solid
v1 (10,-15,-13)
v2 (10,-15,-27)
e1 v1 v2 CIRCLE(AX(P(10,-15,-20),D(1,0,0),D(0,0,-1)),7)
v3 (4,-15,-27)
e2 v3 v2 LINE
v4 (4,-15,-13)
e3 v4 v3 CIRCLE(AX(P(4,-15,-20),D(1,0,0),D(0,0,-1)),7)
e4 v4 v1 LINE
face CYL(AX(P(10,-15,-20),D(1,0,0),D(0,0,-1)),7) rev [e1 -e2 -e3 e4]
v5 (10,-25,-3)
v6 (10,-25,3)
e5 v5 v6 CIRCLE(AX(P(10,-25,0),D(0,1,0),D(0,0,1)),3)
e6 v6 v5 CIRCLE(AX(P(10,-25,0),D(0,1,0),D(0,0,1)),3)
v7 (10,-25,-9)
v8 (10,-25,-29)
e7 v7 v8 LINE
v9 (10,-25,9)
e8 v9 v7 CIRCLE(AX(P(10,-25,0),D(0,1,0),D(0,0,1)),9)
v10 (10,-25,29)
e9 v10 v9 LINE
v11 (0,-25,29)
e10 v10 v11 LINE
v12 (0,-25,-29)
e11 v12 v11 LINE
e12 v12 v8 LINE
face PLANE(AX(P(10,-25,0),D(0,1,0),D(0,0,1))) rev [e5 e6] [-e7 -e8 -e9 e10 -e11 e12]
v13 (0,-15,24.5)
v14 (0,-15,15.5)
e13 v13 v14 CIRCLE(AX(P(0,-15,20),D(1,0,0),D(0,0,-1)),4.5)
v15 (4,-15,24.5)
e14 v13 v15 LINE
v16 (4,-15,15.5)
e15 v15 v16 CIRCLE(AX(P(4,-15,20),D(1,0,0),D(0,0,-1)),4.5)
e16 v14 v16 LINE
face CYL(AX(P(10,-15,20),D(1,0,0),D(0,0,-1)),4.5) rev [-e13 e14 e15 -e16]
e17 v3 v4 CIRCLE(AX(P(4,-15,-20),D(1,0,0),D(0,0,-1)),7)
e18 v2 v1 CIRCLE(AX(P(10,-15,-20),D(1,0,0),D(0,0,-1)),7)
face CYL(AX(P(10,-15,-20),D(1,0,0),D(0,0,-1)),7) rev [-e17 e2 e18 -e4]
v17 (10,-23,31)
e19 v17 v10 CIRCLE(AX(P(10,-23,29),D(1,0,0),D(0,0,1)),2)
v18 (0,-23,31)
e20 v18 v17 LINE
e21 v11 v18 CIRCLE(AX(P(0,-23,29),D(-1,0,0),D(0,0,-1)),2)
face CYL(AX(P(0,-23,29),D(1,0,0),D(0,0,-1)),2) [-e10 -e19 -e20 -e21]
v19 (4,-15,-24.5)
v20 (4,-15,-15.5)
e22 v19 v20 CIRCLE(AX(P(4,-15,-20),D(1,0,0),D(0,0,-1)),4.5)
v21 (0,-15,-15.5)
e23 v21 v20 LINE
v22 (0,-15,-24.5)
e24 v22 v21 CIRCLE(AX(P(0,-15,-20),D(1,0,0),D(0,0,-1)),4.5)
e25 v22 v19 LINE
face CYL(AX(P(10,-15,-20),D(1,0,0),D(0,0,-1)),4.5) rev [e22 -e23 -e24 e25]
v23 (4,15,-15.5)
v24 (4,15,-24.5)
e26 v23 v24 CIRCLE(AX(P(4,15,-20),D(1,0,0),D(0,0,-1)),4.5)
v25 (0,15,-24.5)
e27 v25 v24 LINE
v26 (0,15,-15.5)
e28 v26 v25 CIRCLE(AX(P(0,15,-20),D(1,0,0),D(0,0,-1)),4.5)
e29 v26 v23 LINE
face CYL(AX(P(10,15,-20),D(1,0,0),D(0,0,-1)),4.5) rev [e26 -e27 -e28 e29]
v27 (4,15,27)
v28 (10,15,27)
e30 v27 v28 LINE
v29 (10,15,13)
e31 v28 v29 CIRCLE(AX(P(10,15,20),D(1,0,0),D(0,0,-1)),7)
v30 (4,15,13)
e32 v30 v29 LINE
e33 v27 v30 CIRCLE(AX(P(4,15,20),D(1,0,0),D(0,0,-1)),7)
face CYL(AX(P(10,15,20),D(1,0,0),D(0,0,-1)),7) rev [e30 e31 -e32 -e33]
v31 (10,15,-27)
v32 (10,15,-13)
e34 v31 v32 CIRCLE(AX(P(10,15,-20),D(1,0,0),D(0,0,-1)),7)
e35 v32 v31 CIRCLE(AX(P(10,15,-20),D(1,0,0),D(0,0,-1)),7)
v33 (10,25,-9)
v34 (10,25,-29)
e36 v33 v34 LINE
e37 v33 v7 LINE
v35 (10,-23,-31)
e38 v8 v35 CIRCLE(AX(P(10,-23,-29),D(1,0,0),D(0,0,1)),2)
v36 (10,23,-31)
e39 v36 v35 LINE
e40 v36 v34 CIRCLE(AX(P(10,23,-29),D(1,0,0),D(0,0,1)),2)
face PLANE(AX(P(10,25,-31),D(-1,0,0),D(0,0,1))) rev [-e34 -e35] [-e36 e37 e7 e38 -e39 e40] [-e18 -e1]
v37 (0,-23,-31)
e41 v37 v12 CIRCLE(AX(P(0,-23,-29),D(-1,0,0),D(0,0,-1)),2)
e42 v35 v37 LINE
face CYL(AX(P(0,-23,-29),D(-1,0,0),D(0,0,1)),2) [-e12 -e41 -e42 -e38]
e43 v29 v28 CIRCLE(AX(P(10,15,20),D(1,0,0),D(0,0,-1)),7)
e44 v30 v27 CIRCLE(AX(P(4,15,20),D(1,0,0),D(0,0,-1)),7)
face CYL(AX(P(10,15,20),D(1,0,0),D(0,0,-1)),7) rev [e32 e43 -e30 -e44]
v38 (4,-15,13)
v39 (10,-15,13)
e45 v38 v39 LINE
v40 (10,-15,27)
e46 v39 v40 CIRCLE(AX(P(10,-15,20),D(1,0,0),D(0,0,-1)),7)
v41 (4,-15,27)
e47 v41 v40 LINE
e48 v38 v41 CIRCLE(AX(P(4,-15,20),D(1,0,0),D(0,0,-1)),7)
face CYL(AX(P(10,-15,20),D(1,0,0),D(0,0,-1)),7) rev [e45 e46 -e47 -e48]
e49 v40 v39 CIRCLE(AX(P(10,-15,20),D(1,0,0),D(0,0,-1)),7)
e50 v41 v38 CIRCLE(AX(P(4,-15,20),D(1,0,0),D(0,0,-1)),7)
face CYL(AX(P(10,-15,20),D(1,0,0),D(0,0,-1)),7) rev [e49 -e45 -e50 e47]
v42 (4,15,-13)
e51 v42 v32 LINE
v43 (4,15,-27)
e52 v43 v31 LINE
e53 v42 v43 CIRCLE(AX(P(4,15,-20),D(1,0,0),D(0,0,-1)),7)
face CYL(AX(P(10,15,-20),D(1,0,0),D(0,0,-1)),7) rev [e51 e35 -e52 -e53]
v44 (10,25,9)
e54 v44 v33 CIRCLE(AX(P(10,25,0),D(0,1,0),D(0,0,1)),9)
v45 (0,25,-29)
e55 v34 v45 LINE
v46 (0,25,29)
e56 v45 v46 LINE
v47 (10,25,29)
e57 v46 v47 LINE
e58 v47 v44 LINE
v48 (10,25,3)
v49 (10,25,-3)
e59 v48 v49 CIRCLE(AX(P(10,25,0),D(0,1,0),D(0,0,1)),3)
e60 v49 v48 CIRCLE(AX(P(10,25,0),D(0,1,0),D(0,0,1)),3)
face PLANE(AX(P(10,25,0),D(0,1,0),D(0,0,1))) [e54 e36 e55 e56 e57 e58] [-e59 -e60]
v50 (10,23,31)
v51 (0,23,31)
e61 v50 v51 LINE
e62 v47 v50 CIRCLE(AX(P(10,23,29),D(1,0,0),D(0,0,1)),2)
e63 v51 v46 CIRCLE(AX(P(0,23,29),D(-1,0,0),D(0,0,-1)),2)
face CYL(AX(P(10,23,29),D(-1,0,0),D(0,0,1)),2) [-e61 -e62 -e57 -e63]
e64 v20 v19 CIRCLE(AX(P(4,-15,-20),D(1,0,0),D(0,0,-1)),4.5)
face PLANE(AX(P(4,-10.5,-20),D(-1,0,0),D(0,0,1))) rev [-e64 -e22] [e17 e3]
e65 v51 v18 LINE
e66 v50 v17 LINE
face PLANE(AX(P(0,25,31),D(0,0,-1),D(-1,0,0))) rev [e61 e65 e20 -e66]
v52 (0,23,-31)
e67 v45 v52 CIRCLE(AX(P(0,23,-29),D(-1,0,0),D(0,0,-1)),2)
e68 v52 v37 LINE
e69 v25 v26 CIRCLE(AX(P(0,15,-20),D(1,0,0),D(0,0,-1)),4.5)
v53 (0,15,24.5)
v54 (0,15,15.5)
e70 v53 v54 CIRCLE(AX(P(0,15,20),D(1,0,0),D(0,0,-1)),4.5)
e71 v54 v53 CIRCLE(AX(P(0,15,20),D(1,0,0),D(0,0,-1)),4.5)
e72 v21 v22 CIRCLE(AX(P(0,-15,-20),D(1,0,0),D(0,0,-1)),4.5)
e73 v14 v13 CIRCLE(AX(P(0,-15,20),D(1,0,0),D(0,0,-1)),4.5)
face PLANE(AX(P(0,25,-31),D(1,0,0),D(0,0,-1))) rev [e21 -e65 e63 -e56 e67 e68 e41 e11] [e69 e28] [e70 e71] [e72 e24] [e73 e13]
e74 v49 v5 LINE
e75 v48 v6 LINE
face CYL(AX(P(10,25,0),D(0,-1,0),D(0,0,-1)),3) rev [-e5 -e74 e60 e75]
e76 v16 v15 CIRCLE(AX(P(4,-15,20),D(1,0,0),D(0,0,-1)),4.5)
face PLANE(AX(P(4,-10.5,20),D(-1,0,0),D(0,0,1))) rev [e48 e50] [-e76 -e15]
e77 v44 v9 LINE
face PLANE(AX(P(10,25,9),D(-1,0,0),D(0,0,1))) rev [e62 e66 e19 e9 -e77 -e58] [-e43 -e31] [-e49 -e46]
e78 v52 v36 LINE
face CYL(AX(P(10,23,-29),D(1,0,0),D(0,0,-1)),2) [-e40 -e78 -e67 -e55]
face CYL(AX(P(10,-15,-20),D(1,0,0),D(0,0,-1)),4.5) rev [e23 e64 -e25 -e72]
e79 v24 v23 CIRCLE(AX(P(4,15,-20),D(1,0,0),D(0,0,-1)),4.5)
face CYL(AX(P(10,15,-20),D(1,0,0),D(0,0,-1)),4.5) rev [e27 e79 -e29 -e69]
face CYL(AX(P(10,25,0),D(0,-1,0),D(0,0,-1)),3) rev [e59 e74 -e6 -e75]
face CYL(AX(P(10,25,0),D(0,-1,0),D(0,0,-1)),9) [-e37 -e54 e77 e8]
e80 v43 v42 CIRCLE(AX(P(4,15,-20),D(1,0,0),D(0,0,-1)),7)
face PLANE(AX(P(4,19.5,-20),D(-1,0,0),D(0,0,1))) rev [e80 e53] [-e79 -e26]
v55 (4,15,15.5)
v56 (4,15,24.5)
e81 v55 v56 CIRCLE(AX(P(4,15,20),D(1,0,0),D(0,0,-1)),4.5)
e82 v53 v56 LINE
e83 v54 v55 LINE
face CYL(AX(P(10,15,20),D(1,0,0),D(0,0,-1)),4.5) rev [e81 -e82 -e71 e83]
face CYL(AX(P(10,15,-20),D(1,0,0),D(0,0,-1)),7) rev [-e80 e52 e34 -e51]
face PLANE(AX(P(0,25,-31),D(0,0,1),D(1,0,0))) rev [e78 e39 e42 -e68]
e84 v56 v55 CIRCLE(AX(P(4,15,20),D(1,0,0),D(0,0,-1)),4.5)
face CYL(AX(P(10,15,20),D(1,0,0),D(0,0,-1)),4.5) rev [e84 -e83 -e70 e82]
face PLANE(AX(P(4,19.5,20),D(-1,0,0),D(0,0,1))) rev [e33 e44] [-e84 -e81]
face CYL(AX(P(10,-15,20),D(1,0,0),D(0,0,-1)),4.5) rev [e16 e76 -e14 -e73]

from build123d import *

# Parameters (mm, degrees)
SKETCH_1_R                   = 3
EXTRUDE_1_DEPTH              = 25
HOLE_WIZARD_M8_1_D           = 9
HOLE_WIZARD_M8_1_CBORE_D     = 14
HOLE_WIZARD_M8_1_CBORE_DEPTH = 6
FILLET_1_R                   = 2


with BuildPart() as part:
    # 草图1 → 凸台-拉伸1 (new, symmetric)
    with BuildSketch(Plane(origin=(0, 0, 0), x_dir=(1, 0, 0), z_dir=(0, 1, 0))):
        with BuildLine():
            Line((10, -9), (10, -31))
            Line((10, -31), (0, -31))
            Line((0, -31), (0, 31))
            Line((0, 31), (10, 31))
            Line((10, 31), (10, 9))
            ThreePointArc((10, 9), (19, 0), (10, -9))
        make_face()
        with Locations(Location((10, 0, 0), (0, 0, 270))):
            Circle(SKETCH_1_R, mode=Mode.SUBTRACT)
    extrude(amount=EXTRUDE_1_DEPTH, both=True)

    # M8 六角凹头螺钉的柱形沉头孔1 (through all)
    with Locations(Plane(origin=(10, 0, 0), x_dir=(0, 0, -1), z_dir=(1, 0, 0))):
        with Locations((-20, 15), (-20, -15), (20, -15), (20, 15)):
            CounterBoreHole(HOLE_WIZARD_M8_1_D / 2, HOLE_WIZARD_M8_1_CBORE_D / 2, HOLE_WIZARD_M8_1_CBORE_DEPTH)

    # 圆角1
    fillet_1_edges = [part.edges().sort_by_distance(p)[0] for p in [
        (5, 25, -31),
        (5, -25, -31),
        (5, 25, 31),
        (5, -25, 31),
    ]]
    fillet(fillet_1_edges, radius=FILLET_1_R)


solid = part.part
